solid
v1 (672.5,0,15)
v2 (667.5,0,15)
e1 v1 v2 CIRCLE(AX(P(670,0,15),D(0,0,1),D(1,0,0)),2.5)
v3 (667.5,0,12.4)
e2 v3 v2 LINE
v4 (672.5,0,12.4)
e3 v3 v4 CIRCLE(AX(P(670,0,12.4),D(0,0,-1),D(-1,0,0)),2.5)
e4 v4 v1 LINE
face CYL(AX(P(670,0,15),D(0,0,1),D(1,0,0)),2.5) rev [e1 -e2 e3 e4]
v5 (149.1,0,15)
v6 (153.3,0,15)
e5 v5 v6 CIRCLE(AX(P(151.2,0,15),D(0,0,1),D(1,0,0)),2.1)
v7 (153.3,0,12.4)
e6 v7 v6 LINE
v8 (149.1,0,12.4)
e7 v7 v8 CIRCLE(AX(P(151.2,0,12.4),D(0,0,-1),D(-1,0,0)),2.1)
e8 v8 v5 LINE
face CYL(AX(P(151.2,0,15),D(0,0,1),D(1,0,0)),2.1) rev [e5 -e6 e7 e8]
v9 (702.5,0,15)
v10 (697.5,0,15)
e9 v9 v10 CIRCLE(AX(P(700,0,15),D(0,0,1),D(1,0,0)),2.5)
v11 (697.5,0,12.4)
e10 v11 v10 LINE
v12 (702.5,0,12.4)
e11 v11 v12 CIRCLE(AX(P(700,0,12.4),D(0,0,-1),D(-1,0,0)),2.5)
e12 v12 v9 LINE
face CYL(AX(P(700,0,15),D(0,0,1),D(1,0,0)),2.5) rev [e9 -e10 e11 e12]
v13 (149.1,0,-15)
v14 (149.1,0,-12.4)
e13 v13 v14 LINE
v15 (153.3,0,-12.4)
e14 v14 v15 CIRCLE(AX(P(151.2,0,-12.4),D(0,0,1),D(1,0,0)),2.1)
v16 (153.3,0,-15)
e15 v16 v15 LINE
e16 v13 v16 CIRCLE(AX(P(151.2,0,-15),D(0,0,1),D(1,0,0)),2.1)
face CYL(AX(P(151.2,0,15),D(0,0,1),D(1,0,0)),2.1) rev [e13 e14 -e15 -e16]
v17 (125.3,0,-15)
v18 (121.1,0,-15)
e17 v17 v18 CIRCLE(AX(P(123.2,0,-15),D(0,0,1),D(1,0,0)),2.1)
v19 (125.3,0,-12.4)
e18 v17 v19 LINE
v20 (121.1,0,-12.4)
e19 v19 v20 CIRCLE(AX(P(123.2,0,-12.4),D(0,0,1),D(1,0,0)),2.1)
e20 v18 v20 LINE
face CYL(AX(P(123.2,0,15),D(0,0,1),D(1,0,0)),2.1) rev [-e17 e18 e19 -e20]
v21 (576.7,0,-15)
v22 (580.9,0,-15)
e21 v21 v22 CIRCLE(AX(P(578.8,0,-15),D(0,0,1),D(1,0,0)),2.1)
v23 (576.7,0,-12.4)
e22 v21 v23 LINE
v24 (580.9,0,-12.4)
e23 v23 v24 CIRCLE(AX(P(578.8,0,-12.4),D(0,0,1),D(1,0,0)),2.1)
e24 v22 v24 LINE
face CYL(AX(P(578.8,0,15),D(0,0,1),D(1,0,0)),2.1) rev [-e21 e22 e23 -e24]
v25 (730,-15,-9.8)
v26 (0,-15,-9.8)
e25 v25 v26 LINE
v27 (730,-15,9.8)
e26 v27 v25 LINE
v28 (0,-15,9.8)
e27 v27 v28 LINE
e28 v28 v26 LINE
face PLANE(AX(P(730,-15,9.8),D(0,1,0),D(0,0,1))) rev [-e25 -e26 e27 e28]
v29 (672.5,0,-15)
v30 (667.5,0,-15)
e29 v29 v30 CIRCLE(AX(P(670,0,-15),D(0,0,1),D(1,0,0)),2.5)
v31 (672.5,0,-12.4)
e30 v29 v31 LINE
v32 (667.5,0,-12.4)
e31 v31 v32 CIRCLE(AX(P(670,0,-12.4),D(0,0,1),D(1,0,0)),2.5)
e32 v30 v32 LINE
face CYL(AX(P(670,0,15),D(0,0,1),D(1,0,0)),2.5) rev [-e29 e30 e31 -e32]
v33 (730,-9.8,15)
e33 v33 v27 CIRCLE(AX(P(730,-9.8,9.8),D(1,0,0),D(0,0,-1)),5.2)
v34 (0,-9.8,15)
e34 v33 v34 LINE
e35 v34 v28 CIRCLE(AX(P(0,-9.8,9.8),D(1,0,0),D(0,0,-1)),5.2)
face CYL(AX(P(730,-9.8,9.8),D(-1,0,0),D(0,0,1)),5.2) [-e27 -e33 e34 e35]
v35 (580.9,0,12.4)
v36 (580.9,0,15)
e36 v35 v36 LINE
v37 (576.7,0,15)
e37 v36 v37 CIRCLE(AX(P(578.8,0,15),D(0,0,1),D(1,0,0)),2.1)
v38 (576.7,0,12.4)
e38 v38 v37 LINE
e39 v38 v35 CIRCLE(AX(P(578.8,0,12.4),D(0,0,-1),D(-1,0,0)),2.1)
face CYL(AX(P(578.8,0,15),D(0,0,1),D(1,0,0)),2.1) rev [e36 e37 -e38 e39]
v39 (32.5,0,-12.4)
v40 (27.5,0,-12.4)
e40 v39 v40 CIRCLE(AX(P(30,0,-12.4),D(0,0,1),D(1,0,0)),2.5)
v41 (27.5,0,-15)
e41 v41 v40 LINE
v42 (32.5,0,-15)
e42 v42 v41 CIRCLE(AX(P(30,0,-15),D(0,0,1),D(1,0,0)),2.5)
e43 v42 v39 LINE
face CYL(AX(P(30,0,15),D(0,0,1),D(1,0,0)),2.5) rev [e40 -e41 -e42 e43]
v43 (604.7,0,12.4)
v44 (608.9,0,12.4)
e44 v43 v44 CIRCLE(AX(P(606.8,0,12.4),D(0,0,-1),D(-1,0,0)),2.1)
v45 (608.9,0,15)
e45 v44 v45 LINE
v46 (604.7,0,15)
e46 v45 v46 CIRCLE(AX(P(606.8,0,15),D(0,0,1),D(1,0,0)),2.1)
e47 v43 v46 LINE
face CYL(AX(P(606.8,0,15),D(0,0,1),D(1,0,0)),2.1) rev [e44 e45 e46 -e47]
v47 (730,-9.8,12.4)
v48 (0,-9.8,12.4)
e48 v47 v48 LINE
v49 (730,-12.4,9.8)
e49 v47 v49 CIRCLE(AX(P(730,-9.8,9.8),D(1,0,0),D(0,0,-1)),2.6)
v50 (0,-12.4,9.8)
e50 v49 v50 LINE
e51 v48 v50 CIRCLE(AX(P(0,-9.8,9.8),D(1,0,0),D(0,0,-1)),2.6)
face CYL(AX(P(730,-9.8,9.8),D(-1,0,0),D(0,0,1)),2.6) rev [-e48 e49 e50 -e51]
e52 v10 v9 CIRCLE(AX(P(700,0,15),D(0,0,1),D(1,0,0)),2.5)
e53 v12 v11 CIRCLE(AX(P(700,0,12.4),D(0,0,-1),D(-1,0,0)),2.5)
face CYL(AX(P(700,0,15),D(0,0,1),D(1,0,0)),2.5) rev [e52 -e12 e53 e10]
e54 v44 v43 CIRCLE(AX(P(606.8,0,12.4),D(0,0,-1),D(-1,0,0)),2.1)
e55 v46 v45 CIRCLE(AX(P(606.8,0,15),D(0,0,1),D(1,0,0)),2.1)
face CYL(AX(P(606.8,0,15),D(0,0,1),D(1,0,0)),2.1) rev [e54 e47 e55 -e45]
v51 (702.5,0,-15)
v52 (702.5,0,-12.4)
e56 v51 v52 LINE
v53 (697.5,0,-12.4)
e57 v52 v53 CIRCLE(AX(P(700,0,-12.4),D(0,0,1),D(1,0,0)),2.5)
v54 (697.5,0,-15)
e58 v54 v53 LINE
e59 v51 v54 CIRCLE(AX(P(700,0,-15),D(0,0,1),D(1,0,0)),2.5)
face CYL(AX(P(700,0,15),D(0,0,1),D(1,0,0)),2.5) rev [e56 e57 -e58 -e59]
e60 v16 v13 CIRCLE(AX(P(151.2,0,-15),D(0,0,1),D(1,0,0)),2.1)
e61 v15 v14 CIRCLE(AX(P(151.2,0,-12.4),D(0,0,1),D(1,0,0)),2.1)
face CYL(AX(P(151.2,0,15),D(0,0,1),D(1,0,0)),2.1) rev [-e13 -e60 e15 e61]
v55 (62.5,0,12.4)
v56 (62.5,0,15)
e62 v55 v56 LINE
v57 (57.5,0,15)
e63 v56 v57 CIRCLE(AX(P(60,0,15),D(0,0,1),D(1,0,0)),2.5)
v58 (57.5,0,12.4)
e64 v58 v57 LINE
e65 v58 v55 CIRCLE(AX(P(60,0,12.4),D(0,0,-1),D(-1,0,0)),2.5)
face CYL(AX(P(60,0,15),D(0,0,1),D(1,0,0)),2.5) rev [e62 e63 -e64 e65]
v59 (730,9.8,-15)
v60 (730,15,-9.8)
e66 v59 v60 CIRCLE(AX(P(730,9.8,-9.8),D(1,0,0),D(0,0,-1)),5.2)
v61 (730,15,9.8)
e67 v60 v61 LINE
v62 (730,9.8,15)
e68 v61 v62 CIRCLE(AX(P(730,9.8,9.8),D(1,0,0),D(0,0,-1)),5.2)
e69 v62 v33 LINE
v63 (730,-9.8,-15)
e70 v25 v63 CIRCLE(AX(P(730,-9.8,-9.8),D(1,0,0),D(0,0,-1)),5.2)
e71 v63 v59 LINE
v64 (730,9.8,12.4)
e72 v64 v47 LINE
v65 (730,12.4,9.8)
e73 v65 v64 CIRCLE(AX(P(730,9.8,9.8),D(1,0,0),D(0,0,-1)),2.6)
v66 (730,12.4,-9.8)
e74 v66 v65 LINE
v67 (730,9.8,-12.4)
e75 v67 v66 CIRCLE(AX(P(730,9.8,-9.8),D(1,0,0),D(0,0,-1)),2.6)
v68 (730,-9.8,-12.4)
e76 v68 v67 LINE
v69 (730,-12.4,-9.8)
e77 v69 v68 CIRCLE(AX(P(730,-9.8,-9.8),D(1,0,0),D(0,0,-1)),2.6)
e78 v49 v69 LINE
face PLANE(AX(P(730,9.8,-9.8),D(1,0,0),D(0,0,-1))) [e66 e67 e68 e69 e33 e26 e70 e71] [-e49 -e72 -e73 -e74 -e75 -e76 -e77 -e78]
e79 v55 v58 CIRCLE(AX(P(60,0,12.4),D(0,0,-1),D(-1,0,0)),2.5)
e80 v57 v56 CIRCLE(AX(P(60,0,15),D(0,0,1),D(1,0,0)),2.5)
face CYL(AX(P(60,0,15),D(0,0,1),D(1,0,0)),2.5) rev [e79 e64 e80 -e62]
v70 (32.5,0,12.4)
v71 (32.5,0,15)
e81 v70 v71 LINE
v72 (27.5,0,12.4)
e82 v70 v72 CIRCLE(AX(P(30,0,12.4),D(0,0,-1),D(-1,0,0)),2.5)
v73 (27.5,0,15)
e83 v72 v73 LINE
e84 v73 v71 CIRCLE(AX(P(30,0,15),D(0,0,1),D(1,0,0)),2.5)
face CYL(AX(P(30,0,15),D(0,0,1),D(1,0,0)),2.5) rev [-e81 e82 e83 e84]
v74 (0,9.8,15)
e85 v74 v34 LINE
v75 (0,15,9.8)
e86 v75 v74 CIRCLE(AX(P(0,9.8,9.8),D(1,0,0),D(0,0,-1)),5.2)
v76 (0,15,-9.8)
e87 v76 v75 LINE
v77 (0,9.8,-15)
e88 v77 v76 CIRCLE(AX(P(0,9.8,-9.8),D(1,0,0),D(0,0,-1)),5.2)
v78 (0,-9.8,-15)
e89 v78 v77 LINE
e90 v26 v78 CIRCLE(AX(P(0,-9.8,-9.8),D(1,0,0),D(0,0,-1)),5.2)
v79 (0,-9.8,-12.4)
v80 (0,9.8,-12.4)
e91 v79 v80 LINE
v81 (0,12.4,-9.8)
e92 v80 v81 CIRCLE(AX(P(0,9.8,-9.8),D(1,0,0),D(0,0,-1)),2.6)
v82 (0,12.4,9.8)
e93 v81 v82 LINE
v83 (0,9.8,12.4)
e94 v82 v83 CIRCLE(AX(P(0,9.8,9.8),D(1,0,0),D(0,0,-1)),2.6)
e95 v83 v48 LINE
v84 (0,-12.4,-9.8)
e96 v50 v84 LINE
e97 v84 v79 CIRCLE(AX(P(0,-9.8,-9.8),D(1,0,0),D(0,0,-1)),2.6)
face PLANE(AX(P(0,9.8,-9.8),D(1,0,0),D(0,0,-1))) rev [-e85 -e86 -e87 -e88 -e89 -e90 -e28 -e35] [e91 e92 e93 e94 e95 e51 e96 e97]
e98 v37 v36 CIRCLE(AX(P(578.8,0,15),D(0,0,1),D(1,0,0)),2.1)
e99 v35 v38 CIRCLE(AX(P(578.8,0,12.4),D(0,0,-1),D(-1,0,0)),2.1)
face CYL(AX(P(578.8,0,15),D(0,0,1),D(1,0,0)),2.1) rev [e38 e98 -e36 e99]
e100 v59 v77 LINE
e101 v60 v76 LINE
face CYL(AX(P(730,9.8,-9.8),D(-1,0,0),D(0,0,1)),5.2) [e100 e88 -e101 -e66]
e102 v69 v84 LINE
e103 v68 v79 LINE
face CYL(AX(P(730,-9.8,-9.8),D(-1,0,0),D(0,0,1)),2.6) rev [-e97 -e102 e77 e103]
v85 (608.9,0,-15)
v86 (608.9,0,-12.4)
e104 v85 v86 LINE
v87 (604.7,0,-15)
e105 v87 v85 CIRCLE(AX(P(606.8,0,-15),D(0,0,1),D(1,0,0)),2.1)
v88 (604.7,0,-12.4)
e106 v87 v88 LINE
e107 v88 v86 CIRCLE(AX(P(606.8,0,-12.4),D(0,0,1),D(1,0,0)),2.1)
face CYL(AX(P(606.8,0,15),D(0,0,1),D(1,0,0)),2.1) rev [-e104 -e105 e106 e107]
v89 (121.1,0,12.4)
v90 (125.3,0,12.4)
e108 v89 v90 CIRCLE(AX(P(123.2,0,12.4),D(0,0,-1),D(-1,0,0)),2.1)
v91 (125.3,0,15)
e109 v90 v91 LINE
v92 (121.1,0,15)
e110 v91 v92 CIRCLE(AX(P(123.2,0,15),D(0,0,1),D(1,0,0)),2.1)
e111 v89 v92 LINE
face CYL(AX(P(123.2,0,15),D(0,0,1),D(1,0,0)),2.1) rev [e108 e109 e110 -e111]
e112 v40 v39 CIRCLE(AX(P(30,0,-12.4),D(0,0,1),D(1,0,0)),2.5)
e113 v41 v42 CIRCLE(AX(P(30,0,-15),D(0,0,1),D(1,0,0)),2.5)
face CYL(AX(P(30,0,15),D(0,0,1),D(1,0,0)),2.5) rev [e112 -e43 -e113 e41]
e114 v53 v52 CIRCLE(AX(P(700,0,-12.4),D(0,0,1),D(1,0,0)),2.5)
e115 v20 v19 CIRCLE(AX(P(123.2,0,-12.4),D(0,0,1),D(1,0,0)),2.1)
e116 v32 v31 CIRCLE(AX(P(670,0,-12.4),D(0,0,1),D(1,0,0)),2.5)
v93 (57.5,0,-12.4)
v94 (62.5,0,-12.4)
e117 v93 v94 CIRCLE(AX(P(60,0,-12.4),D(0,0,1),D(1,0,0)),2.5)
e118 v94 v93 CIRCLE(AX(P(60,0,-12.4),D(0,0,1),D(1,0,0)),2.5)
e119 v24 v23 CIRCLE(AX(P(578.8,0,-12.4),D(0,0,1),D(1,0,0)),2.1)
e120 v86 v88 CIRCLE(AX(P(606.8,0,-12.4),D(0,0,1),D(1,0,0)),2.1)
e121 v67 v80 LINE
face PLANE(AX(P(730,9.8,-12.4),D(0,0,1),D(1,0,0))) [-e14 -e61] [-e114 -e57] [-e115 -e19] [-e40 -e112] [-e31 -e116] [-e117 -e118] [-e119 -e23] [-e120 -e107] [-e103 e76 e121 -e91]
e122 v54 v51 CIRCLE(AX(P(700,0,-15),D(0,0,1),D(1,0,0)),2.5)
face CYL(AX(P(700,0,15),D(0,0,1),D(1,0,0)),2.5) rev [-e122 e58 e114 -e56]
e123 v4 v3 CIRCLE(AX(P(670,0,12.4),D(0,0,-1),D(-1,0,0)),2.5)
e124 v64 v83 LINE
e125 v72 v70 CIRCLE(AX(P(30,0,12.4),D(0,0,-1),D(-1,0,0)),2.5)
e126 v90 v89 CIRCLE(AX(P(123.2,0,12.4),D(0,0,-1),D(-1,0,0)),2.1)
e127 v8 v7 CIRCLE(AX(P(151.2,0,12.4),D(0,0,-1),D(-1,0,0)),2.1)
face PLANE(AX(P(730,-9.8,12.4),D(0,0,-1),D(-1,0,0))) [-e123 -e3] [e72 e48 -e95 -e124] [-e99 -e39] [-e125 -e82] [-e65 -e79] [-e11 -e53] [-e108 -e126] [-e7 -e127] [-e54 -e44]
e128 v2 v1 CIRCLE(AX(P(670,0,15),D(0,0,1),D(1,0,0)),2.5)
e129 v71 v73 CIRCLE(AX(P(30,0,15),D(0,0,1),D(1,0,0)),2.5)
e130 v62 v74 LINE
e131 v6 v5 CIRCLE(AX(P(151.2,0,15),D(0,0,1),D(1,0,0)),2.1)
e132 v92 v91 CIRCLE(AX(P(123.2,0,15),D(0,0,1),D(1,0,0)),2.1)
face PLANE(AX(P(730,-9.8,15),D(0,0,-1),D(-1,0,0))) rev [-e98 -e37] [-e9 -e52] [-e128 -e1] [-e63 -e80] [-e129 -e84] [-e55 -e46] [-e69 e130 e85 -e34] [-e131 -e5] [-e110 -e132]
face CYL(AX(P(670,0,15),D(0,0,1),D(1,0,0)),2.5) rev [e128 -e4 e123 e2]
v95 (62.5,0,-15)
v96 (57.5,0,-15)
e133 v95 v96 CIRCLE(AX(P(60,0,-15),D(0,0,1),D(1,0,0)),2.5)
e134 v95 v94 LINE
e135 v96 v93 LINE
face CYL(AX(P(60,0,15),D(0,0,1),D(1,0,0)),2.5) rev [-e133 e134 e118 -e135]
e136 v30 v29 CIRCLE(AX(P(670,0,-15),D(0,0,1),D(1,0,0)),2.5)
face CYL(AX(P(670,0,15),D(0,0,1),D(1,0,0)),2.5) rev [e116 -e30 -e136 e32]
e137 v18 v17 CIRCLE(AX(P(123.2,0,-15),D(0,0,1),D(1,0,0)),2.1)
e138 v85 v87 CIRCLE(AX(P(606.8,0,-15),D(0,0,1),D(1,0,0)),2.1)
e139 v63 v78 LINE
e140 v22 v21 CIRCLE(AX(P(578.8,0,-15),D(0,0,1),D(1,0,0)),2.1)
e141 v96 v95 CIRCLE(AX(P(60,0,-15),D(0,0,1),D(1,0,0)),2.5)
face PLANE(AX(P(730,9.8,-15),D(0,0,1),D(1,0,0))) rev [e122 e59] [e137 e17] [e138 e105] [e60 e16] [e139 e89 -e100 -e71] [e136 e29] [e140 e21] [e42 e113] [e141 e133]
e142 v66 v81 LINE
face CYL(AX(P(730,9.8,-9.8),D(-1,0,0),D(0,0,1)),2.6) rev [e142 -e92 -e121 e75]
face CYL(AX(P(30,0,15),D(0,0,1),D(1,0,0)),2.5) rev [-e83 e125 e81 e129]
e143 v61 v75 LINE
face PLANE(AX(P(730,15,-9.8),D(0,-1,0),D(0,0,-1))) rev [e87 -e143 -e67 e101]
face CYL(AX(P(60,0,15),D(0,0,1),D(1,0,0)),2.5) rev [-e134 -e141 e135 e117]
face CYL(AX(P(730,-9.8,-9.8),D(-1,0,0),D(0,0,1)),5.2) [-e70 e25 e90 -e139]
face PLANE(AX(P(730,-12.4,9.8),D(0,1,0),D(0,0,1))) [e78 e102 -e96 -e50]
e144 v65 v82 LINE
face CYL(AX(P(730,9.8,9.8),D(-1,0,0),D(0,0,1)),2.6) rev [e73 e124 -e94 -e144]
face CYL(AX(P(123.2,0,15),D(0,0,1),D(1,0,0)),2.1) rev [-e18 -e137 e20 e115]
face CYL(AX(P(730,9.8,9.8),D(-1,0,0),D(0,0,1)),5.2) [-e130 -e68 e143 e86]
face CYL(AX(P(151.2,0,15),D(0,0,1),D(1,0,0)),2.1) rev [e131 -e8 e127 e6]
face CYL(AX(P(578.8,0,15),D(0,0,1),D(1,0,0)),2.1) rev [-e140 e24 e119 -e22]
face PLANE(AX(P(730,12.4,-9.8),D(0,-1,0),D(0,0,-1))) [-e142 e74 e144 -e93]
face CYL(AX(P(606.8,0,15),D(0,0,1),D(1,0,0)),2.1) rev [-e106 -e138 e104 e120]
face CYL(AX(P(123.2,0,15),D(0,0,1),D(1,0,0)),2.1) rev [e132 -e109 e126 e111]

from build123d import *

# Parameters (mm, degrees)
MEMBER_1_DEPTH     = 730
HOLE_WIZARD_M5_1_D = 4.2
HOLE_WIZARD_M6_1_D = 5


with BuildPart() as part:
    # Sketch1 → Member 1 (new body)
    with BuildSketch(Plane(origin=(0, 0, 0), x_dir=(0, 0, -1), z_dir=(1, 0, 0))):
        with BuildLine():
            Line((-9.8, -15), (9.8, -15))
            ThreePointArc((9.8, -15), (13.476955262, -13.476955262), (15, -9.8))
            Line((15, -9.8), (15, 9.8))
            ThreePointArc((15, 9.8), (13.476955262, 13.476955262), (9.8, 15))
            Line((9.8, 15), (-9.8, 15))
            ThreePointArc((-9.8, 15), (-13.476955262, 13.476955262), (-15, 9.8))
            Line((-15, 9.8), (-15, -9.8))
            ThreePointArc((-15, -9.8), (-13.476955262, -13.476955262), (-9.8, -15))
        make_face()
        with BuildLine():
            Line((-9.8, -12.4), (9.8, -12.4))
            ThreePointArc((9.8, -12.4), (11.638477631, -11.638477631), (12.4, -9.8))
            Line((12.4, -9.8), (12.4, 9.8))
            ThreePointArc((12.4, 9.8), (11.638477631, 11.638477631), (9.8, 12.4))
            Line((9.8, 12.4), (-9.8, 12.4))
            ThreePointArc((-9.8, 12.4), (-11.638477631, 11.638477631), (-12.4, 9.8))
            Line((-12.4, 9.8), (-12.4, -9.8))
            ThreePointArc((-12.4, -9.8), (-11.638477631, -11.638477631), (-9.8, -12.4))
        make_face(mode=Mode.SUBTRACT)
    extrude(amount=MEMBER_1_DEPTH)

    # M5 螺纹孔1 (through all)
    with Locations(Plane.XY.offset(15)):
        with Locations((123.2, 0), (151.2, 0), (606.8, 0), (578.8, 0)):
            Hole(HOLE_WIZARD_M5_1_D / 2)

    # M6 螺纹孔1 (through all)
    with Locations(Plane.XY.offset(15)):
        with Locations((30, 0), (60, 0), (700, 0), (670, 0)):
            Hole(HOLE_WIZARD_M6_1_D / 2)


solid = part.part
